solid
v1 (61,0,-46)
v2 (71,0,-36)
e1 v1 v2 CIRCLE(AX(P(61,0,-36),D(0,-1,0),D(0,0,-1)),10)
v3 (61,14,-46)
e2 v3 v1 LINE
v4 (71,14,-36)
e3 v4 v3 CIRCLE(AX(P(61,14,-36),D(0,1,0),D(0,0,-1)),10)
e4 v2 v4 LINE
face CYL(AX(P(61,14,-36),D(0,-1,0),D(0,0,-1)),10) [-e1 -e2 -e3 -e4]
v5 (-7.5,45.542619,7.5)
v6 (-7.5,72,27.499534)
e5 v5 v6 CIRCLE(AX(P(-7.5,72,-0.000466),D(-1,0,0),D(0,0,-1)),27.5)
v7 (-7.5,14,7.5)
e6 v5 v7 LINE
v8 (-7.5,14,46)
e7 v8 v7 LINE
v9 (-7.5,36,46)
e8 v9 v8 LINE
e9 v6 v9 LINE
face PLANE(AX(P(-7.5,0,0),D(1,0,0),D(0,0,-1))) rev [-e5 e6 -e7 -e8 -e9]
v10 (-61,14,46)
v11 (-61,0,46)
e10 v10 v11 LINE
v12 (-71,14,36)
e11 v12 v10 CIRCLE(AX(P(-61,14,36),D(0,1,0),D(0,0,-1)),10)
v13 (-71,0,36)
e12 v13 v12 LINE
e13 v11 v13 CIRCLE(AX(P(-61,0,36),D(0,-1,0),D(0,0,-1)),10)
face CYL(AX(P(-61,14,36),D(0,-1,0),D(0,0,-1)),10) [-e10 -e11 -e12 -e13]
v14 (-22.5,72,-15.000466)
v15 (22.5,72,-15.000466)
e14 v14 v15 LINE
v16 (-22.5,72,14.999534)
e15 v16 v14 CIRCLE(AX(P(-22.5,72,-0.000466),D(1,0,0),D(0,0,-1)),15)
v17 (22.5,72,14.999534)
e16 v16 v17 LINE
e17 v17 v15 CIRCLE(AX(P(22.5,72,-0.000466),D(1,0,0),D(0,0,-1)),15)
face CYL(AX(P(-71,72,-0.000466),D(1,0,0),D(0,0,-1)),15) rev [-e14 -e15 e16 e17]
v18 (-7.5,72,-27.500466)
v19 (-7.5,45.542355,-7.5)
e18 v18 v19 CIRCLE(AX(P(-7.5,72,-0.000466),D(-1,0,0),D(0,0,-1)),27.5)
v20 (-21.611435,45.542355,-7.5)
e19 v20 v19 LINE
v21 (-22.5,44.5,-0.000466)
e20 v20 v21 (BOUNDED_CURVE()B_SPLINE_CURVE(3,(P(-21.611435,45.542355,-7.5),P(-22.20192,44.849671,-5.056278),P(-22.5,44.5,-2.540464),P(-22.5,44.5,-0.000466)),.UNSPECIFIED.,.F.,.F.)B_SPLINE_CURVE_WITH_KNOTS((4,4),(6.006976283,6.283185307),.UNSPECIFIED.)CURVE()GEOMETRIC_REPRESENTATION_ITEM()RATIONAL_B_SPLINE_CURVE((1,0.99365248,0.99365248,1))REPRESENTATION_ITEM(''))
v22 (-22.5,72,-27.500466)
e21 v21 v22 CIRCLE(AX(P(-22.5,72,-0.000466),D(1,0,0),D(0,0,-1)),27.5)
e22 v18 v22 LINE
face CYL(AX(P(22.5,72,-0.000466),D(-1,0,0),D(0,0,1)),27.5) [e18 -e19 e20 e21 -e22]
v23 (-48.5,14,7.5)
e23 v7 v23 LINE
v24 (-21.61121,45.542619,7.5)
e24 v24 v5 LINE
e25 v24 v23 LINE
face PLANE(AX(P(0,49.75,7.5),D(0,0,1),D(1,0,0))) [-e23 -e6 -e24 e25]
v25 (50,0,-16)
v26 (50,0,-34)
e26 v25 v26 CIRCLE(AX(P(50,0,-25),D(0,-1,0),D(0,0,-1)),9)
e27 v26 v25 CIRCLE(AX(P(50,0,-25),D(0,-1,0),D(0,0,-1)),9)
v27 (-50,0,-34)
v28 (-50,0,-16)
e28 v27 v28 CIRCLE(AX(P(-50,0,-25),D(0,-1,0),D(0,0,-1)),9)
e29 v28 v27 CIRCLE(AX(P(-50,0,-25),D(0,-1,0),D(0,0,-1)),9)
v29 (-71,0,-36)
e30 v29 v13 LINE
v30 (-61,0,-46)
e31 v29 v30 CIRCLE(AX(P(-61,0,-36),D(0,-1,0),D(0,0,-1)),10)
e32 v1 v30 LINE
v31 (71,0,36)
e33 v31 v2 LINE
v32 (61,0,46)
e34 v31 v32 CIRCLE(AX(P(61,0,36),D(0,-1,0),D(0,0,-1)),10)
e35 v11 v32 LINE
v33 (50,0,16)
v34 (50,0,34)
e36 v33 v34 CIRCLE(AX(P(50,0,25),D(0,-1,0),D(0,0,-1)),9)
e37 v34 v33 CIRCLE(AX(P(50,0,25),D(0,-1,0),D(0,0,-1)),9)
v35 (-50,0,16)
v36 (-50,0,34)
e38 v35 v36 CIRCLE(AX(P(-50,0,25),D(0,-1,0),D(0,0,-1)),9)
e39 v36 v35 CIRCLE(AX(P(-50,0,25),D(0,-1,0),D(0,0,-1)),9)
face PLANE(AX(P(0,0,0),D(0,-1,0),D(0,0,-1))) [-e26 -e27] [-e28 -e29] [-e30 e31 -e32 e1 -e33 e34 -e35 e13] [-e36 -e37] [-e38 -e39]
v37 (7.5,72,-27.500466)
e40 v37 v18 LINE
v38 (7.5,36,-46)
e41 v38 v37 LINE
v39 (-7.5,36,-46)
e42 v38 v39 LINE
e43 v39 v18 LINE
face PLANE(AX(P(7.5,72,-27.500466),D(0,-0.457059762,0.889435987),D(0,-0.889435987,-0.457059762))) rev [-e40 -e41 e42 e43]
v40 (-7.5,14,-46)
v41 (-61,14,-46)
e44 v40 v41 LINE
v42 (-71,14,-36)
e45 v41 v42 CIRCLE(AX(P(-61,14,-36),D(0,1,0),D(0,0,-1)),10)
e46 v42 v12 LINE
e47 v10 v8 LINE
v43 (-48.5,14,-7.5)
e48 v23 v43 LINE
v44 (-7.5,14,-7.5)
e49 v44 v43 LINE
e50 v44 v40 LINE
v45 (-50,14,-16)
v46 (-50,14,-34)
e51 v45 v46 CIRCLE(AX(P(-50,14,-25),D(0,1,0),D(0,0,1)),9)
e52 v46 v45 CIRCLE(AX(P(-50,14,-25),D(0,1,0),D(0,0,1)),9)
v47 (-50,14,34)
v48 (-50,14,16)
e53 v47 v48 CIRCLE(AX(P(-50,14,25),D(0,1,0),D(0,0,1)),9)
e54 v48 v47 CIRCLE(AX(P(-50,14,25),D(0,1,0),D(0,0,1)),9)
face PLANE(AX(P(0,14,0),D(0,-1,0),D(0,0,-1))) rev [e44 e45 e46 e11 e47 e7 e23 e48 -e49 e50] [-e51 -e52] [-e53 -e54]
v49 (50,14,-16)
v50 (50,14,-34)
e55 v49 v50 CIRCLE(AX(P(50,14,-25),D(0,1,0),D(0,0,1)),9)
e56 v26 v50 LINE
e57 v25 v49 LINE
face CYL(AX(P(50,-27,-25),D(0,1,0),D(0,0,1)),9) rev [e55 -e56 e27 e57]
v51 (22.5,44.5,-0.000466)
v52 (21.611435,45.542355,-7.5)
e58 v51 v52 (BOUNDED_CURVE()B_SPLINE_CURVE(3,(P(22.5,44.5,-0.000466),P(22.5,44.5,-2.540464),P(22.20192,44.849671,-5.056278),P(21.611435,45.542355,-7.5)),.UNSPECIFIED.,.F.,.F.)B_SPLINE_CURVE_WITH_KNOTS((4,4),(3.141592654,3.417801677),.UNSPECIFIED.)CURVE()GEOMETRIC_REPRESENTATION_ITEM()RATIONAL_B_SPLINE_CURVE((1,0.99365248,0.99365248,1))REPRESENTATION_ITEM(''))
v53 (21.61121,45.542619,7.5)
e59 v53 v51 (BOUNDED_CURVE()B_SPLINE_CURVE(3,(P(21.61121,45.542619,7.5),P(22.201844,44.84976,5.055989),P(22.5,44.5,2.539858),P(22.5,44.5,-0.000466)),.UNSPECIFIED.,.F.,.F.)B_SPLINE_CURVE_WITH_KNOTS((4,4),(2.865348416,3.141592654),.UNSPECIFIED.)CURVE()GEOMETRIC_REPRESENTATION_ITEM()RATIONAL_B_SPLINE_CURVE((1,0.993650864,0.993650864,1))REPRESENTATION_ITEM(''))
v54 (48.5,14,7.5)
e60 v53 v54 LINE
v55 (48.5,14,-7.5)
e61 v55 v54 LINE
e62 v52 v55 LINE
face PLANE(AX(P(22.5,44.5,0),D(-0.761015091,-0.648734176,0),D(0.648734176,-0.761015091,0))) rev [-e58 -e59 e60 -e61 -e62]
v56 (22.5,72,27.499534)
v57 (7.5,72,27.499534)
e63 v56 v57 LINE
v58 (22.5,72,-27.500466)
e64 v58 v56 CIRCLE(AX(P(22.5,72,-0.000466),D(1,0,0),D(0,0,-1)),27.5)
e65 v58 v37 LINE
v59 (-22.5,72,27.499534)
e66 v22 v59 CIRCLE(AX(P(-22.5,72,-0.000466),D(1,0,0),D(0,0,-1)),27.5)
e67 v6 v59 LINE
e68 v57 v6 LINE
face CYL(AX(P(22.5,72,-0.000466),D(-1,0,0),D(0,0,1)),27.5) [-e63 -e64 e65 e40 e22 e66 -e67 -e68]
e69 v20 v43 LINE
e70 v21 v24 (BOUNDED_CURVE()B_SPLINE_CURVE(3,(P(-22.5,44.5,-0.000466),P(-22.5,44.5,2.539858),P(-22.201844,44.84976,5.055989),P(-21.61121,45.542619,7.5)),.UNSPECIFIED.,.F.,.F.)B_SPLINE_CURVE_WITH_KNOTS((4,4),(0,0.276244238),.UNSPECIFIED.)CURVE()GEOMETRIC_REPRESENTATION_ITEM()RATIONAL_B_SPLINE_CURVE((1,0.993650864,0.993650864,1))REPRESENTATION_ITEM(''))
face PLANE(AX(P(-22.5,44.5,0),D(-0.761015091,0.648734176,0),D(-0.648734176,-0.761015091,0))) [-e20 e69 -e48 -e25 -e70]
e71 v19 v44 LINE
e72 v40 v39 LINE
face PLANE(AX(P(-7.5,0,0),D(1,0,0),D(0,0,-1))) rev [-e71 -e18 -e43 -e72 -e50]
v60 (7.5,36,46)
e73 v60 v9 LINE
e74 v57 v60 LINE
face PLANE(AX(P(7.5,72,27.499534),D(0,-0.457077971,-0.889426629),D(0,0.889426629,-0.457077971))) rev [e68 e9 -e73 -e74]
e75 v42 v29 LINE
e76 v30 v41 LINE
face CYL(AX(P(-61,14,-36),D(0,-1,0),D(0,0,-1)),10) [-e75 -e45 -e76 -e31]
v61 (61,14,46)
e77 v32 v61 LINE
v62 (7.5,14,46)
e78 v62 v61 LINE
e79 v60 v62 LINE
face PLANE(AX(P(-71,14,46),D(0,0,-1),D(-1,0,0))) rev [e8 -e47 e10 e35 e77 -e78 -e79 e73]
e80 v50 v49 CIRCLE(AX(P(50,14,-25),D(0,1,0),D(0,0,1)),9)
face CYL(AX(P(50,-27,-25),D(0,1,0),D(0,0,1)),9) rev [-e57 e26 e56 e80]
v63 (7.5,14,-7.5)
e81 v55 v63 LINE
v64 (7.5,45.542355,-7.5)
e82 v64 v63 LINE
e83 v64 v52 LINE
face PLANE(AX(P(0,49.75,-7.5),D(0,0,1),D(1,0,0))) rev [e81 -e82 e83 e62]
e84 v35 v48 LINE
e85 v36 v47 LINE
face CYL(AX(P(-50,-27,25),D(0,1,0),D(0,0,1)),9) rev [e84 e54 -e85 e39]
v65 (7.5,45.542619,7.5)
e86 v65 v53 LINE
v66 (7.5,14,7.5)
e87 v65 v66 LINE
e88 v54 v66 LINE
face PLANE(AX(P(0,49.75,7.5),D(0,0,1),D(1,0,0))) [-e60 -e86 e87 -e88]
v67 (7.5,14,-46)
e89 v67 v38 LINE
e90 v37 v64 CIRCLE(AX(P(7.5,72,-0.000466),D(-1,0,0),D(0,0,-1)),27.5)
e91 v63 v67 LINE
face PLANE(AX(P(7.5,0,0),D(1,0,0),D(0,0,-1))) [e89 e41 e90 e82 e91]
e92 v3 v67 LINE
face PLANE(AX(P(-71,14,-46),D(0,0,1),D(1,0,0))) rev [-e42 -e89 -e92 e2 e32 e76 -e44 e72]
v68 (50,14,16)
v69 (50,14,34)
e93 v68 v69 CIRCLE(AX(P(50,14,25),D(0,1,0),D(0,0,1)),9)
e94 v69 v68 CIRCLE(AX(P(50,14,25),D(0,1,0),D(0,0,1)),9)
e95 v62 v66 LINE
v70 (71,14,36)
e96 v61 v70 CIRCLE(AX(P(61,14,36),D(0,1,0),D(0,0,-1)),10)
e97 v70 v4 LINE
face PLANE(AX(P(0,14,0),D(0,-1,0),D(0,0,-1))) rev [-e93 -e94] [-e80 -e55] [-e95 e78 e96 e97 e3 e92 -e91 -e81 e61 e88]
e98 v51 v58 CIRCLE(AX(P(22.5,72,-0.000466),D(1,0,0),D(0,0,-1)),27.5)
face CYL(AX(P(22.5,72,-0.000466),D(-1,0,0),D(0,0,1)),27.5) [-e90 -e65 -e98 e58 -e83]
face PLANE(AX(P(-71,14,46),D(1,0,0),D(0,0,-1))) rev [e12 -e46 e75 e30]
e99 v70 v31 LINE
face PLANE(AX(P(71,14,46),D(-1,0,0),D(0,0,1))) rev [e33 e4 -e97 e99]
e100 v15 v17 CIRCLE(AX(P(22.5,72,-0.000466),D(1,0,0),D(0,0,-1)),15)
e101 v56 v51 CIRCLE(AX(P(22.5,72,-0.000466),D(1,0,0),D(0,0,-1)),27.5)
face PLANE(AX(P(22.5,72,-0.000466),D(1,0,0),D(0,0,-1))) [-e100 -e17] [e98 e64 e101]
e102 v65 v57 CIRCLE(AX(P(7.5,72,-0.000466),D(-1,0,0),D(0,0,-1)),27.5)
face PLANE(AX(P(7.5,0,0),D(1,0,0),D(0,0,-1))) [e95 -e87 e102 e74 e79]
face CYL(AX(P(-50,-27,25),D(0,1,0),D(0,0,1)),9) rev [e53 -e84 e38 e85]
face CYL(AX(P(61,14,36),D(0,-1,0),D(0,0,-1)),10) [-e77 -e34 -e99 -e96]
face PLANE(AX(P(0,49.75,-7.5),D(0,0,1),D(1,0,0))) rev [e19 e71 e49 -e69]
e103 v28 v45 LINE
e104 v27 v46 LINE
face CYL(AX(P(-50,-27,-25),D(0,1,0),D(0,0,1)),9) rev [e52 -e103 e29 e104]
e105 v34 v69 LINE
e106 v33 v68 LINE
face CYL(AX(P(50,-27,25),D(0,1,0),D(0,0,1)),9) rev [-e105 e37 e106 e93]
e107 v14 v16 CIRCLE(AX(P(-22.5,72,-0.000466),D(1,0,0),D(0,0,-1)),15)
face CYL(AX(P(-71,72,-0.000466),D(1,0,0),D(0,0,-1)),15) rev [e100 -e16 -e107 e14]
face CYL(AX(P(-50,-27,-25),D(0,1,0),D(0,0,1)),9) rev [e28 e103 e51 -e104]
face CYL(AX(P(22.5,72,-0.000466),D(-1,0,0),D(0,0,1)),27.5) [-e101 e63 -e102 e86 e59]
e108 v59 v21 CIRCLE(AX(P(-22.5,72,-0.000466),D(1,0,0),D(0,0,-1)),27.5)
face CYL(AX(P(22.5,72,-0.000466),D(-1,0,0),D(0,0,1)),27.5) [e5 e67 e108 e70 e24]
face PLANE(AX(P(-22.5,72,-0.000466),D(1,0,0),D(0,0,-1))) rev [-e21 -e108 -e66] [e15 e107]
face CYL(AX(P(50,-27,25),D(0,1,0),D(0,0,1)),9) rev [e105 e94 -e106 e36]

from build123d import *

# Parameters (mm, degrees)
BASE_PLATE_SKETCH_W         = 142
BASE_PLATE_SKETCH_H         = 92
BASE_PLATE_142X92X14_DEPTH  = 14
BASE_CORNER_FILLETS_R10_R   = 10
BEARING_PEDESTAL_DEPTH      = 7.5
BEARING_BOSS_SKETCH_R       = 27.5
BEARING_BOSS_55_DEPTH       = 22.5
BORE_SKETCH_R               = 15
BORE_30_DEPTH               = 145.078103819
SUPPORT_RIB_1_REACH         = 132.603
SUPPORT_RIB_1_SKETCH_WALL_W = 303.284863468
SUPPORT_RIB_1_SKETCH_WALL_H = 15
SUPPORT_RIB_2_REACH         = 132.603
SUPPORT_RIB_2_SKETCH_WALL_W = 303.284863468
SUPPORT_RIB_2_SKETCH_WALL_H = 15
MOUNTING_HOLES_SKETCH_R     = 9
MOUNTING_HOLES_4X_18_DEPTH  = 41


with BuildPart() as part:
    # Base Plate Sketch → Base Plate 142x92x14 (new body)
    with BuildSketch(Plane(origin=(0, 0, 0), x_dir=(1, 0, 0), z_dir=(0, 1, 0))):
        Rectangle(BASE_PLATE_SKETCH_W, BASE_PLATE_SKETCH_H)
    extrude(amount=BASE_PLATE_142X92X14_DEPTH)

    # Base Corner Fillets R10
    base_corner_fillets_r10_edges = [part.edges().sort_by_distance(p)[0] for p in [
        (71, 7, 46),
        (-71, 7, 46),
        (-71, 7, -46),
        (71, 7, -46),
    ]]
    fillet(base_corner_fillets_r10_edges, radius=BASE_CORNER_FILLETS_R10_R)

    # Pedestal Sketch → Bearing Pedestal (add, symmetric)
    with BuildSketch(Plane(origin=(0, 0, 0), x_dir=(0, 0, -1), z_dir=(1, 0, 0))):
        Polygon((46, 14), (46, 36), (27.50046584, 72), (-27.49953416, 72), (-46, 36), (-46, 14), align=None)
    extrude(amount=BEARING_PEDESTAL_DEPTH, both=True)

    # Bearing Boss Sketch → Bearing Boss Ø55 (add, symmetric)
    with BuildSketch(Plane(origin=(0, 0, 0), x_dir=(0, 0, -1), z_dir=(1, 0, 0))):
        with Locations((0.00046584, 72)):
            Circle(BEARING_BOSS_SKETCH_R)
    extrude(amount=BEARING_BOSS_55_DEPTH, both=True)

    # Bore Sketch → Bore Ø30 (cut, through all)
    with BuildSketch(Plane(origin=(22.5, 0, 0), x_dir=(0, 0, -1), z_dir=(1, 0, 0))):
        with Locations((0.00046584, 72)):
            Circle(BORE_SKETCH_R)
    extrude(amount=-BORE_30_DEPTH, mode=Mode.SUBTRACT)

    # Support Rib 1 Sketch wall → Support Rib 1 (add, up to next)
    with BuildSketch(Plane(origin=(35.5, 29.25, 0), x_dir=(0.648734176014, -0.761015091093, 0), z_dir=(0.761015091093, 0.648734176014, 0)), mode=Mode.PRIVATE) as support_rib_1_sk1:
        Rectangle(SUPPORT_RIB_1_SKETCH_WALL_W, SUPPORT_RIB_1_SKETCH_WALL_H)
    support_rib_1_tool1 = extrude(support_rib_1_sk1.sketch, amount=-SUPPORT_RIB_1_REACH, mode=Mode.PRIVATE) - part.part
    add(support_rib_1_tool1.solids().sort_by_distance((35.5, 29.25, 0))[0])

    # Support Rib 2 Sketch wall → Support Rib 2 (add, up to next)
    with BuildSketch(Plane(origin=(-35.5, 29.25, 0), x_dir=(-0.648734176014, -0.761015091093, 0), z_dir=(0.761015091093, -0.648734176014, 0)), mode=Mode.PRIVATE) as support_rib_2_sk1:
        Rectangle(SUPPORT_RIB_2_SKETCH_WALL_W, SUPPORT_RIB_2_SKETCH_WALL_H)
    support_rib_2_tool1 = extrude(support_rib_2_sk1.sketch, amount=SUPPORT_RIB_2_REACH, mode=Mode.PRIVATE) - part.part
    add(support_rib_2_tool1.solids().sort_by_distance((-35.5, 29.25, 0))[0])

    # Mounting Holes Sketch → Mounting Holes 4xØ18 (cut)
    with BuildSketch(Plane(origin=(0, 14, 0), x_dir=(1, 0, 0), z_dir=(0, 1, 0))):
        with Locations(Location((-50, 25, 0), (0, 0, 270))):
            Circle(MOUNTING_HOLES_SKETCH_R)
        with Locations(Location((50, 25, 0), (0, 0, 270))):
            Circle(MOUNTING_HOLES_SKETCH_R)
        with Locations(Location((50, -25, 0), (0, 0, 270))):
            Circle(MOUNTING_HOLES_SKETCH_R)
        with Locations(Location((-50, -25, 0), (0, 0, 270))):
            Circle(MOUNTING_HOLES_SKETCH_R)
    extrude(amount=-MOUNTING_HOLES_4X_18_DEPTH, mode=Mode.SUBTRACT)


solid = part.part
